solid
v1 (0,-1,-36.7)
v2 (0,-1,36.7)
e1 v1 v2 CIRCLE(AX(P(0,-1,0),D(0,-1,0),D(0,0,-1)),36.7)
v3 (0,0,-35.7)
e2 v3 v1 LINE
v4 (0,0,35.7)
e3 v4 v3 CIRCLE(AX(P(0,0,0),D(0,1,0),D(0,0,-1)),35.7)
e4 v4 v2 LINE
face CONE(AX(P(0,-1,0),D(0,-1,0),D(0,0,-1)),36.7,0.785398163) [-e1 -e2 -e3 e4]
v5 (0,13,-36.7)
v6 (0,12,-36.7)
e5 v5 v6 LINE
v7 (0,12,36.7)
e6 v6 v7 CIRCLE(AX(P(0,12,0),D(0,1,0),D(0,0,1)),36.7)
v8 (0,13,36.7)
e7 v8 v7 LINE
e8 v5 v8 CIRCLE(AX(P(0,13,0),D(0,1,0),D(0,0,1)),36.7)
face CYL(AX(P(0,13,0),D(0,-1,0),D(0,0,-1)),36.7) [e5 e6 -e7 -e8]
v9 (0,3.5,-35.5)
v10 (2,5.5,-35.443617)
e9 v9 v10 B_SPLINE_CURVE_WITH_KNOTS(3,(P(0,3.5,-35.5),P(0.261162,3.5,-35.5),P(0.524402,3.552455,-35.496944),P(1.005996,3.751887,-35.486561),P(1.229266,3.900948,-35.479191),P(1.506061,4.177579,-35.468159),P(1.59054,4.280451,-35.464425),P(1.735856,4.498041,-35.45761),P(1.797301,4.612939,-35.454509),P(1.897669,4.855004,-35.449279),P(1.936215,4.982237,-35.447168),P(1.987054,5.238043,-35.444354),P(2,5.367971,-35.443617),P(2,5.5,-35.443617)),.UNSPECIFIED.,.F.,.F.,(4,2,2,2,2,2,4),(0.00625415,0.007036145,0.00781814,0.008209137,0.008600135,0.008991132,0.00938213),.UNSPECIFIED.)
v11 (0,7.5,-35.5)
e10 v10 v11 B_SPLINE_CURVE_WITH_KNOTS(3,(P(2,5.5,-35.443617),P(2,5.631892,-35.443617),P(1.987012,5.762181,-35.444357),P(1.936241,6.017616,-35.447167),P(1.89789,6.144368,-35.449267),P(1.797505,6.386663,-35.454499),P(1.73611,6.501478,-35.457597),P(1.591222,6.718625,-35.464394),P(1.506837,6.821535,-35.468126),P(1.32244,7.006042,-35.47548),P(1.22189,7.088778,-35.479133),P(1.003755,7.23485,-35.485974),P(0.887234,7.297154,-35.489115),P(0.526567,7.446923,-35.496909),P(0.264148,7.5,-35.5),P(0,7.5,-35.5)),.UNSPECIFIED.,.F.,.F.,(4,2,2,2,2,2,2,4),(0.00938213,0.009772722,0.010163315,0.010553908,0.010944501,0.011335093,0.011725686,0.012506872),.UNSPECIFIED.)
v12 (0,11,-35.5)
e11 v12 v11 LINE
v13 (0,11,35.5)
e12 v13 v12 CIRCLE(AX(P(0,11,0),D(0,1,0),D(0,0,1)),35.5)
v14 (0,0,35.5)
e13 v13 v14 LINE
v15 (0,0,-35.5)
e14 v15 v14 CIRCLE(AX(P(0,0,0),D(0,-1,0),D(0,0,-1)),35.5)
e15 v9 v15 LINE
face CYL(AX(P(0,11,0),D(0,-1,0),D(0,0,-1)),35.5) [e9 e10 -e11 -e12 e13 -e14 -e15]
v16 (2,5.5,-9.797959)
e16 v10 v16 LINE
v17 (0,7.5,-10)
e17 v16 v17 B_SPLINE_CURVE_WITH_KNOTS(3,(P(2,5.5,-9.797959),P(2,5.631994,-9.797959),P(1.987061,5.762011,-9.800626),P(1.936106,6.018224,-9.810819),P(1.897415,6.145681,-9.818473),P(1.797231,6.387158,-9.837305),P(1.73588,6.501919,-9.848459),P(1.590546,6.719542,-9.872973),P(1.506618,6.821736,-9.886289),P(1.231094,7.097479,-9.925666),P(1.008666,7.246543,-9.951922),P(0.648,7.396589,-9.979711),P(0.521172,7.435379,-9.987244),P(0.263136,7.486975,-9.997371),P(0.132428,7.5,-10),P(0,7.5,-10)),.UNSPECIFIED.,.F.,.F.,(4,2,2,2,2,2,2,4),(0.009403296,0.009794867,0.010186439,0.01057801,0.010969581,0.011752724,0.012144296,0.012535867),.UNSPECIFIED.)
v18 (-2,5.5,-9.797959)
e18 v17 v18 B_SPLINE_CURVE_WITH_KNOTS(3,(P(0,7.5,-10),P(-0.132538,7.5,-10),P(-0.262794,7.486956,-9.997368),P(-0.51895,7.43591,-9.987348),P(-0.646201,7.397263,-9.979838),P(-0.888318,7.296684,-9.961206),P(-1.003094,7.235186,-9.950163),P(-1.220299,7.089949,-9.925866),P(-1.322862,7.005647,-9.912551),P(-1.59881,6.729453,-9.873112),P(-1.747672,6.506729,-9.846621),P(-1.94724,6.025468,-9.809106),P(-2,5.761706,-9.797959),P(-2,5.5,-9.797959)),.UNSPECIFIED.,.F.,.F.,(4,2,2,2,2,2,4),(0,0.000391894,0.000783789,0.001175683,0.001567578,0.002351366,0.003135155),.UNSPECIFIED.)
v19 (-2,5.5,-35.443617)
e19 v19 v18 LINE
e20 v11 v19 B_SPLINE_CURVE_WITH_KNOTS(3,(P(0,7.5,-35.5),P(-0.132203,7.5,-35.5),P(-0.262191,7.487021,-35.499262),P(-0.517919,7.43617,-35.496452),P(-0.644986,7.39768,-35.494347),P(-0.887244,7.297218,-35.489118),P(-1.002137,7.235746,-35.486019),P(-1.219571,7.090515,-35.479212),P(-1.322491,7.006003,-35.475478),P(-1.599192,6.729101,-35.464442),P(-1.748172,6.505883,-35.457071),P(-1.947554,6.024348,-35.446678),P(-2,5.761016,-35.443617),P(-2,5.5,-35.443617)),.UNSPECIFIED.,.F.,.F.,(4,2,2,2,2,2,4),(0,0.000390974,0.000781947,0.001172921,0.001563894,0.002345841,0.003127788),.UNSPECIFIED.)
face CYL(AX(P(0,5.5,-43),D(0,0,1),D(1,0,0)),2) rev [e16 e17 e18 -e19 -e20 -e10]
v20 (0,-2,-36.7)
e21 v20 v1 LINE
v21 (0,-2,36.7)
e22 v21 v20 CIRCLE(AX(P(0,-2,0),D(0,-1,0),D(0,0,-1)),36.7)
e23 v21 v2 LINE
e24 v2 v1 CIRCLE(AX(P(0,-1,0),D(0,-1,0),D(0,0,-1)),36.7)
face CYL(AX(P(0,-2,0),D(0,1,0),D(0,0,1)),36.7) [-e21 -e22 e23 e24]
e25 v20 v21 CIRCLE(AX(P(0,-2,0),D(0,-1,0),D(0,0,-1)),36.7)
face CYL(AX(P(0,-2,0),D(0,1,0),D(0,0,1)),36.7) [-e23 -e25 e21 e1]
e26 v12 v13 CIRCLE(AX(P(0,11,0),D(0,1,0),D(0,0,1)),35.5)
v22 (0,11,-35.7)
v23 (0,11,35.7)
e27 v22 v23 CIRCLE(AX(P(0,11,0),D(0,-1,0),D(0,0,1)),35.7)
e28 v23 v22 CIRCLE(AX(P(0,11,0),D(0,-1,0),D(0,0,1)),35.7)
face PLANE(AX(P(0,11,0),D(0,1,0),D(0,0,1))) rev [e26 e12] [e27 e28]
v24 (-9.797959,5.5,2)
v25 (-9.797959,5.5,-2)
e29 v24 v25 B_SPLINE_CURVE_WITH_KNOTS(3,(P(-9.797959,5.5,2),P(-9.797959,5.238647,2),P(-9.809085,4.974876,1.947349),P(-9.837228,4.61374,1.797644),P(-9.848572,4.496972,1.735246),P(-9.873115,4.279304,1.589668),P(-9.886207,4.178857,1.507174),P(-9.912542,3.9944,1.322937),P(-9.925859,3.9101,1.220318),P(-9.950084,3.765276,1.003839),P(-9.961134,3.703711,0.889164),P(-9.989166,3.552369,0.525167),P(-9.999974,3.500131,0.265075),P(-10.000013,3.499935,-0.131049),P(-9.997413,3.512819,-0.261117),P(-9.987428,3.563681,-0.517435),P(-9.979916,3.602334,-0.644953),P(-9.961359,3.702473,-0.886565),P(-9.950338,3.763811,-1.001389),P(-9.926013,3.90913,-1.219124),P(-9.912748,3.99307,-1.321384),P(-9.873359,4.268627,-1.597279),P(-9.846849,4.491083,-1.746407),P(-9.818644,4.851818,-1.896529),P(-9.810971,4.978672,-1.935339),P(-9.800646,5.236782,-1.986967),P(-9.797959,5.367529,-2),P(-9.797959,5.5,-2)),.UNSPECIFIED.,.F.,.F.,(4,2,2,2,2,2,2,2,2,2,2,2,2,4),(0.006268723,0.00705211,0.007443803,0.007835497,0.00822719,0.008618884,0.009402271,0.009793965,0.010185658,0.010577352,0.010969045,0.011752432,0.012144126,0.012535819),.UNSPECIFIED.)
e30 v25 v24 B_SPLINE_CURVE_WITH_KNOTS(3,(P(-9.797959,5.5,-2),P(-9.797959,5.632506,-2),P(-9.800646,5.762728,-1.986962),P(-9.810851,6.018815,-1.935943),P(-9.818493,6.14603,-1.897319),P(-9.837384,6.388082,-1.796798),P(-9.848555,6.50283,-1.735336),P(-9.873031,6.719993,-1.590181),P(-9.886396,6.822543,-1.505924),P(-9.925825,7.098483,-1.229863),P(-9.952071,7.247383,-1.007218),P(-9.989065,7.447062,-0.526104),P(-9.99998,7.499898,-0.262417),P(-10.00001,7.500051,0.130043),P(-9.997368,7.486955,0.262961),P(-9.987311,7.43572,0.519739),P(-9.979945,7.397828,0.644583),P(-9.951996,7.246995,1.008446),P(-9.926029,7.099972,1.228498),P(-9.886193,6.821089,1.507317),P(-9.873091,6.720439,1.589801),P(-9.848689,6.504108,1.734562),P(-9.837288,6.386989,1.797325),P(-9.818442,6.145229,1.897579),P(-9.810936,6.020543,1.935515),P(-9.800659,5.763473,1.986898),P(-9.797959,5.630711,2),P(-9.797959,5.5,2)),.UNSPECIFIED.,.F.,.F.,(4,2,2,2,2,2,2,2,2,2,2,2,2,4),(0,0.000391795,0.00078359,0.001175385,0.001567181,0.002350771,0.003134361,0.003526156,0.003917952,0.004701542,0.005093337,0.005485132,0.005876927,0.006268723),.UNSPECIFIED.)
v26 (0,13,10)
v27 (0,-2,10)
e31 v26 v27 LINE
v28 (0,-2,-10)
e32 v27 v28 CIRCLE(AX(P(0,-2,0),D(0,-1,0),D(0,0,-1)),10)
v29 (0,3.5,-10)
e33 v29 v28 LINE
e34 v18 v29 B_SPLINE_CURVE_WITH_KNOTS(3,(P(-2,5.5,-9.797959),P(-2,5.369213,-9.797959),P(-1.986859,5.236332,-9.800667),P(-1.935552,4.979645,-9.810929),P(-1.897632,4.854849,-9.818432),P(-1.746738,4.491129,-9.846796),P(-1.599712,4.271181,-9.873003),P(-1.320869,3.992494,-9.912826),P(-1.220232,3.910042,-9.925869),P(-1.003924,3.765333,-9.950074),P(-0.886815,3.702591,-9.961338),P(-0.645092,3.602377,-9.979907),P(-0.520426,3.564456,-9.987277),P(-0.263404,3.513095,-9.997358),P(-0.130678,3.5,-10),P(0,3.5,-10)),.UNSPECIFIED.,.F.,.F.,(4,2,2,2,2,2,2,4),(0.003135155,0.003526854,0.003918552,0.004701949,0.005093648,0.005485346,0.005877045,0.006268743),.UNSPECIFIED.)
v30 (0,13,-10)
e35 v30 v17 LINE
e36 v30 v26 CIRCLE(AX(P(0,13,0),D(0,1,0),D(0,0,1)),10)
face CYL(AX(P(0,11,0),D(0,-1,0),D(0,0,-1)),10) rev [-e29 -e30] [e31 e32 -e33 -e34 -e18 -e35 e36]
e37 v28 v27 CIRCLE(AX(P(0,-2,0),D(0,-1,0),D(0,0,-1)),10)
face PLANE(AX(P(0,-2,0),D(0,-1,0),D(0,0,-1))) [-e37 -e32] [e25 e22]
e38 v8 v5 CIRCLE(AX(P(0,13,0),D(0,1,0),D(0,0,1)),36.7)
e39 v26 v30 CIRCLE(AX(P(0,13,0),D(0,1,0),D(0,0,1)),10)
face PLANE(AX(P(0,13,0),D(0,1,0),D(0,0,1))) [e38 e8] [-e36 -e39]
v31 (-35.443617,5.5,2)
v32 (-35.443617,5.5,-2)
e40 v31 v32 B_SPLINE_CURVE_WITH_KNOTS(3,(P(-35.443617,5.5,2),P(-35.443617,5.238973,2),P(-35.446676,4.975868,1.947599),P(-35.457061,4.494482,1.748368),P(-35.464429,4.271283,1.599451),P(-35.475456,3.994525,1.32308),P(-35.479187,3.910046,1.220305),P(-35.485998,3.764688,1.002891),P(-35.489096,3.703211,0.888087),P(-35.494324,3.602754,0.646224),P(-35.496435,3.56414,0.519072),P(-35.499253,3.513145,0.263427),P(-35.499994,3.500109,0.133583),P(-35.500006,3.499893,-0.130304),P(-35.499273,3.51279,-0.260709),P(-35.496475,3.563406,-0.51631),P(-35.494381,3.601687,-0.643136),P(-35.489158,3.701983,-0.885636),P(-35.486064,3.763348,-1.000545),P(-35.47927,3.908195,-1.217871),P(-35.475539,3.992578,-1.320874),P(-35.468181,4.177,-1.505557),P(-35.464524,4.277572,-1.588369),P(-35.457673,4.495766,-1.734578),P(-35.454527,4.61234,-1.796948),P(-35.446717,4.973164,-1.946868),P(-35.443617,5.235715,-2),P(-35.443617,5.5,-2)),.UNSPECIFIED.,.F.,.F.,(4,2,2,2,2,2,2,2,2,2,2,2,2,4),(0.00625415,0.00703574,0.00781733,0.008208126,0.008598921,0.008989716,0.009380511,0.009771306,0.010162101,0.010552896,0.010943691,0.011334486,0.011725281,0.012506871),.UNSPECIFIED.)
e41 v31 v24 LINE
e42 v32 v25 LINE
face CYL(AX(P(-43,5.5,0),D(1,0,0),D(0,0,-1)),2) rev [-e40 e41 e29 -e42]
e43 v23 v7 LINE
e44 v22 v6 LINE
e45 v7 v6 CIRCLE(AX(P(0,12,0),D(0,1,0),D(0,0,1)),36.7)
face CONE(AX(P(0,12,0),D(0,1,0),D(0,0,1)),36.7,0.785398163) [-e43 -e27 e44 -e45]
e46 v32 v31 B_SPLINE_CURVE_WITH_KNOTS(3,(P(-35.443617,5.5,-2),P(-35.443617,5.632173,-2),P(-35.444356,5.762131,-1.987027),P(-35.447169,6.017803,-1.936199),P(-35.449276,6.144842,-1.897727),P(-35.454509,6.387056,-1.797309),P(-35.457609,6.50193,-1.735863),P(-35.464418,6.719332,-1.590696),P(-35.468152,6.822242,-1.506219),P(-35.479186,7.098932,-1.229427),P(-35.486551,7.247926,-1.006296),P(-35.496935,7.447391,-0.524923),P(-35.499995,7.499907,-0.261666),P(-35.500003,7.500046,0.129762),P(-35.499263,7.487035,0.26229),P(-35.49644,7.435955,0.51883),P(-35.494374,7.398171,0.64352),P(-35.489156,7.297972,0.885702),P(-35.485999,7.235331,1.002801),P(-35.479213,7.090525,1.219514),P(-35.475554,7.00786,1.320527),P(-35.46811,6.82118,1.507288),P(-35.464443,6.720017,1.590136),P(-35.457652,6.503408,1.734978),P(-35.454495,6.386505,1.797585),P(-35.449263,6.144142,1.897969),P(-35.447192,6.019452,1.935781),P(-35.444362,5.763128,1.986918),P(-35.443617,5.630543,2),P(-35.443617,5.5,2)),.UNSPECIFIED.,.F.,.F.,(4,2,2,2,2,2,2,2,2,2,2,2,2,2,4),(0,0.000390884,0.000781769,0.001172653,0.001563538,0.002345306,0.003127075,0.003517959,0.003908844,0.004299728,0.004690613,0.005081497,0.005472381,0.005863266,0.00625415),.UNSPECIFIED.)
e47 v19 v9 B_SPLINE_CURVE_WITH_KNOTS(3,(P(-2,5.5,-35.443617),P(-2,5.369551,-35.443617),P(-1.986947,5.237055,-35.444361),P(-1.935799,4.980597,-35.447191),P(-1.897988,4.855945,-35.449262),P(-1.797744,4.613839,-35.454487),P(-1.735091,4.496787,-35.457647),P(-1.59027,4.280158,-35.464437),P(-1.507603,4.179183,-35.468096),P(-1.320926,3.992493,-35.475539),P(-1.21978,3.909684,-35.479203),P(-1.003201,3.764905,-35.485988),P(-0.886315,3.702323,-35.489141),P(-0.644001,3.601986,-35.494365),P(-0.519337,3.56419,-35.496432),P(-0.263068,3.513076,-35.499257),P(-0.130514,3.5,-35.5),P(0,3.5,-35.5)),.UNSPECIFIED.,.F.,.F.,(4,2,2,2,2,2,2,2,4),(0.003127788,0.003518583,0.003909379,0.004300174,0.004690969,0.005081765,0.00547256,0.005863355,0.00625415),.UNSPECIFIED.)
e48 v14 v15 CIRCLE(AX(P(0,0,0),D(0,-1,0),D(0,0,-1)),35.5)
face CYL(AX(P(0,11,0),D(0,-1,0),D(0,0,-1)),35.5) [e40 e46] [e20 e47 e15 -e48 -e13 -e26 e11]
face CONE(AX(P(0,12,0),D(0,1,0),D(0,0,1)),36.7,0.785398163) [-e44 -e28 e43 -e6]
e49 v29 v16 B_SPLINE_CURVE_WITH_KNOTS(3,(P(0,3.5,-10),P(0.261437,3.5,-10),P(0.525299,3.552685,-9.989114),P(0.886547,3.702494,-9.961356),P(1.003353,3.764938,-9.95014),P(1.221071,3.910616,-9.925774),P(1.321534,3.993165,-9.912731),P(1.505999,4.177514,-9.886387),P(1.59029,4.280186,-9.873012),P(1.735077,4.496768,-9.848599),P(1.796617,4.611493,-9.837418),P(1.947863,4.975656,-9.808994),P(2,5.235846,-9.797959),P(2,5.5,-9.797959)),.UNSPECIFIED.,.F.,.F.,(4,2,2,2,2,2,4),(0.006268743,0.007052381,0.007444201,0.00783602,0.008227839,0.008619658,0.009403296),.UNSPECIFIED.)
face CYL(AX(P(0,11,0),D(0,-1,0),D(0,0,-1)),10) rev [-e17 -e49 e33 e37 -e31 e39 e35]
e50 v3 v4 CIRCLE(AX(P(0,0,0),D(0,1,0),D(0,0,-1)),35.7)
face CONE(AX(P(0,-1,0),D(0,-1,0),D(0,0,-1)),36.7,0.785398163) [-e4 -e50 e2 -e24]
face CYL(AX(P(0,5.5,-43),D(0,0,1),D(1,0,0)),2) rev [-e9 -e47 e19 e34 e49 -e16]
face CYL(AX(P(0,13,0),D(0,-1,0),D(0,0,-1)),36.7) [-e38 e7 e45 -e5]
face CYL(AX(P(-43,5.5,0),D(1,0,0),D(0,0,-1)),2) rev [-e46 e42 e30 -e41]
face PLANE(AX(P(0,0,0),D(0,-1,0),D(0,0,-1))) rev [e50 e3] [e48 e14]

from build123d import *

# Parameters (mm, degrees)
SKETCH1_R           = 35.5
SKETCH1_R_2         = 10
BOSS_EXTRUDE1_DEPTH = 11
SKETCH2_R           = 36.7
SKETCH2_R_2         = 10
BOSS_EXTRUDE2_DEPTH = 2
BOSS_EXTRUDE3_START = 2
SKETCH3_R           = 36.7
SKETCH3_R_2         = 10
BOSS_EXTRUDE3_DEPTH = 2
CHAMFER1_SIZE       = 1
SKETCH5_R           = 2
CUT_EXTRUDE1_DEPTH  = 43
SKETCH6_R           = 2
CUT_EXTRUDE2_DEPTH  = 43


with BuildPart() as part:
    # Sketch1 → Boss-Extrude1 (new body)
    with BuildSketch(Plane(origin=(0, 0, 0), x_dir=(1, 0, 0), z_dir=(0, 1, 0))):
        with Locations(Location((0, 0, 0), (0, 0, 270))):
            Circle(SKETCH1_R)
        with Locations(Location((0, 0, 0), (0, 0, 270))):
            Circle(SKETCH1_R_2, mode=Mode.SUBTRACT)
    extrude(amount=BOSS_EXTRUDE1_DEPTH)

    # Sketch2 → Boss-Extrude2 (add)
    with BuildSketch(Plane(origin=(0, 11, 0), x_dir=(1, 0, 0), z_dir=(0, 1, 0))):
        with Locations(Location((0, 0, 0), (0, 0, 270))):
            Circle(SKETCH2_R)
        with Locations(Location((0, 0, 0), (0, 0, 270))):
            Circle(SKETCH2_R_2, mode=Mode.SUBTRACT)
    extrude(amount=BOSS_EXTRUDE2_DEPTH)

    # Sketch3 → Boss-Extrude3 (add)
    with BuildSketch(Plane.XZ.offset(BOSS_EXTRUDE3_START)):
        with Locations(Location((0, 0, 0), (0, 0, 90))):
            Circle(SKETCH3_R)
        with Locations(Location((0, 0, 0), (0, 0, 270))):
            Circle(SKETCH3_R_2, mode=Mode.SUBTRACT)
    extrude(amount=-BOSS_EXTRUDE3_DEPTH)

    # Chamfer1
    chamfer1_edges = [part.edges().sort_by_distance(p)[0] for p in [
        (0, 11, -36.7),
        (0, 0, -36.7),
    ]]
    chamfer(chamfer1_edges, length=CHAMFER1_SIZE)

    # Sketch5 → Cut-Extrude1 (cut)
    with BuildSketch(Plane.XY):
        with Locations(Location((0, 5.5, 0), (0, 0, 90))):
            Circle(SKETCH5_R)
    extrude(amount=-CUT_EXTRUDE1_DEPTH, mode=Mode.SUBTRACT)

    # Sketch6 → Cut-Extrude2 (cut)
    with BuildSketch(Plane(origin=(0, 0, 0), x_dir=(0, 0, -1), z_dir=(1, 0, 0))):
        with Locations((0, 5.5)):
            Circle(SKETCH6_R)
    extrude(amount=-CUT_EXTRUDE2_DEPTH, mode=Mode.SUBTRACT)


solid = part.part
